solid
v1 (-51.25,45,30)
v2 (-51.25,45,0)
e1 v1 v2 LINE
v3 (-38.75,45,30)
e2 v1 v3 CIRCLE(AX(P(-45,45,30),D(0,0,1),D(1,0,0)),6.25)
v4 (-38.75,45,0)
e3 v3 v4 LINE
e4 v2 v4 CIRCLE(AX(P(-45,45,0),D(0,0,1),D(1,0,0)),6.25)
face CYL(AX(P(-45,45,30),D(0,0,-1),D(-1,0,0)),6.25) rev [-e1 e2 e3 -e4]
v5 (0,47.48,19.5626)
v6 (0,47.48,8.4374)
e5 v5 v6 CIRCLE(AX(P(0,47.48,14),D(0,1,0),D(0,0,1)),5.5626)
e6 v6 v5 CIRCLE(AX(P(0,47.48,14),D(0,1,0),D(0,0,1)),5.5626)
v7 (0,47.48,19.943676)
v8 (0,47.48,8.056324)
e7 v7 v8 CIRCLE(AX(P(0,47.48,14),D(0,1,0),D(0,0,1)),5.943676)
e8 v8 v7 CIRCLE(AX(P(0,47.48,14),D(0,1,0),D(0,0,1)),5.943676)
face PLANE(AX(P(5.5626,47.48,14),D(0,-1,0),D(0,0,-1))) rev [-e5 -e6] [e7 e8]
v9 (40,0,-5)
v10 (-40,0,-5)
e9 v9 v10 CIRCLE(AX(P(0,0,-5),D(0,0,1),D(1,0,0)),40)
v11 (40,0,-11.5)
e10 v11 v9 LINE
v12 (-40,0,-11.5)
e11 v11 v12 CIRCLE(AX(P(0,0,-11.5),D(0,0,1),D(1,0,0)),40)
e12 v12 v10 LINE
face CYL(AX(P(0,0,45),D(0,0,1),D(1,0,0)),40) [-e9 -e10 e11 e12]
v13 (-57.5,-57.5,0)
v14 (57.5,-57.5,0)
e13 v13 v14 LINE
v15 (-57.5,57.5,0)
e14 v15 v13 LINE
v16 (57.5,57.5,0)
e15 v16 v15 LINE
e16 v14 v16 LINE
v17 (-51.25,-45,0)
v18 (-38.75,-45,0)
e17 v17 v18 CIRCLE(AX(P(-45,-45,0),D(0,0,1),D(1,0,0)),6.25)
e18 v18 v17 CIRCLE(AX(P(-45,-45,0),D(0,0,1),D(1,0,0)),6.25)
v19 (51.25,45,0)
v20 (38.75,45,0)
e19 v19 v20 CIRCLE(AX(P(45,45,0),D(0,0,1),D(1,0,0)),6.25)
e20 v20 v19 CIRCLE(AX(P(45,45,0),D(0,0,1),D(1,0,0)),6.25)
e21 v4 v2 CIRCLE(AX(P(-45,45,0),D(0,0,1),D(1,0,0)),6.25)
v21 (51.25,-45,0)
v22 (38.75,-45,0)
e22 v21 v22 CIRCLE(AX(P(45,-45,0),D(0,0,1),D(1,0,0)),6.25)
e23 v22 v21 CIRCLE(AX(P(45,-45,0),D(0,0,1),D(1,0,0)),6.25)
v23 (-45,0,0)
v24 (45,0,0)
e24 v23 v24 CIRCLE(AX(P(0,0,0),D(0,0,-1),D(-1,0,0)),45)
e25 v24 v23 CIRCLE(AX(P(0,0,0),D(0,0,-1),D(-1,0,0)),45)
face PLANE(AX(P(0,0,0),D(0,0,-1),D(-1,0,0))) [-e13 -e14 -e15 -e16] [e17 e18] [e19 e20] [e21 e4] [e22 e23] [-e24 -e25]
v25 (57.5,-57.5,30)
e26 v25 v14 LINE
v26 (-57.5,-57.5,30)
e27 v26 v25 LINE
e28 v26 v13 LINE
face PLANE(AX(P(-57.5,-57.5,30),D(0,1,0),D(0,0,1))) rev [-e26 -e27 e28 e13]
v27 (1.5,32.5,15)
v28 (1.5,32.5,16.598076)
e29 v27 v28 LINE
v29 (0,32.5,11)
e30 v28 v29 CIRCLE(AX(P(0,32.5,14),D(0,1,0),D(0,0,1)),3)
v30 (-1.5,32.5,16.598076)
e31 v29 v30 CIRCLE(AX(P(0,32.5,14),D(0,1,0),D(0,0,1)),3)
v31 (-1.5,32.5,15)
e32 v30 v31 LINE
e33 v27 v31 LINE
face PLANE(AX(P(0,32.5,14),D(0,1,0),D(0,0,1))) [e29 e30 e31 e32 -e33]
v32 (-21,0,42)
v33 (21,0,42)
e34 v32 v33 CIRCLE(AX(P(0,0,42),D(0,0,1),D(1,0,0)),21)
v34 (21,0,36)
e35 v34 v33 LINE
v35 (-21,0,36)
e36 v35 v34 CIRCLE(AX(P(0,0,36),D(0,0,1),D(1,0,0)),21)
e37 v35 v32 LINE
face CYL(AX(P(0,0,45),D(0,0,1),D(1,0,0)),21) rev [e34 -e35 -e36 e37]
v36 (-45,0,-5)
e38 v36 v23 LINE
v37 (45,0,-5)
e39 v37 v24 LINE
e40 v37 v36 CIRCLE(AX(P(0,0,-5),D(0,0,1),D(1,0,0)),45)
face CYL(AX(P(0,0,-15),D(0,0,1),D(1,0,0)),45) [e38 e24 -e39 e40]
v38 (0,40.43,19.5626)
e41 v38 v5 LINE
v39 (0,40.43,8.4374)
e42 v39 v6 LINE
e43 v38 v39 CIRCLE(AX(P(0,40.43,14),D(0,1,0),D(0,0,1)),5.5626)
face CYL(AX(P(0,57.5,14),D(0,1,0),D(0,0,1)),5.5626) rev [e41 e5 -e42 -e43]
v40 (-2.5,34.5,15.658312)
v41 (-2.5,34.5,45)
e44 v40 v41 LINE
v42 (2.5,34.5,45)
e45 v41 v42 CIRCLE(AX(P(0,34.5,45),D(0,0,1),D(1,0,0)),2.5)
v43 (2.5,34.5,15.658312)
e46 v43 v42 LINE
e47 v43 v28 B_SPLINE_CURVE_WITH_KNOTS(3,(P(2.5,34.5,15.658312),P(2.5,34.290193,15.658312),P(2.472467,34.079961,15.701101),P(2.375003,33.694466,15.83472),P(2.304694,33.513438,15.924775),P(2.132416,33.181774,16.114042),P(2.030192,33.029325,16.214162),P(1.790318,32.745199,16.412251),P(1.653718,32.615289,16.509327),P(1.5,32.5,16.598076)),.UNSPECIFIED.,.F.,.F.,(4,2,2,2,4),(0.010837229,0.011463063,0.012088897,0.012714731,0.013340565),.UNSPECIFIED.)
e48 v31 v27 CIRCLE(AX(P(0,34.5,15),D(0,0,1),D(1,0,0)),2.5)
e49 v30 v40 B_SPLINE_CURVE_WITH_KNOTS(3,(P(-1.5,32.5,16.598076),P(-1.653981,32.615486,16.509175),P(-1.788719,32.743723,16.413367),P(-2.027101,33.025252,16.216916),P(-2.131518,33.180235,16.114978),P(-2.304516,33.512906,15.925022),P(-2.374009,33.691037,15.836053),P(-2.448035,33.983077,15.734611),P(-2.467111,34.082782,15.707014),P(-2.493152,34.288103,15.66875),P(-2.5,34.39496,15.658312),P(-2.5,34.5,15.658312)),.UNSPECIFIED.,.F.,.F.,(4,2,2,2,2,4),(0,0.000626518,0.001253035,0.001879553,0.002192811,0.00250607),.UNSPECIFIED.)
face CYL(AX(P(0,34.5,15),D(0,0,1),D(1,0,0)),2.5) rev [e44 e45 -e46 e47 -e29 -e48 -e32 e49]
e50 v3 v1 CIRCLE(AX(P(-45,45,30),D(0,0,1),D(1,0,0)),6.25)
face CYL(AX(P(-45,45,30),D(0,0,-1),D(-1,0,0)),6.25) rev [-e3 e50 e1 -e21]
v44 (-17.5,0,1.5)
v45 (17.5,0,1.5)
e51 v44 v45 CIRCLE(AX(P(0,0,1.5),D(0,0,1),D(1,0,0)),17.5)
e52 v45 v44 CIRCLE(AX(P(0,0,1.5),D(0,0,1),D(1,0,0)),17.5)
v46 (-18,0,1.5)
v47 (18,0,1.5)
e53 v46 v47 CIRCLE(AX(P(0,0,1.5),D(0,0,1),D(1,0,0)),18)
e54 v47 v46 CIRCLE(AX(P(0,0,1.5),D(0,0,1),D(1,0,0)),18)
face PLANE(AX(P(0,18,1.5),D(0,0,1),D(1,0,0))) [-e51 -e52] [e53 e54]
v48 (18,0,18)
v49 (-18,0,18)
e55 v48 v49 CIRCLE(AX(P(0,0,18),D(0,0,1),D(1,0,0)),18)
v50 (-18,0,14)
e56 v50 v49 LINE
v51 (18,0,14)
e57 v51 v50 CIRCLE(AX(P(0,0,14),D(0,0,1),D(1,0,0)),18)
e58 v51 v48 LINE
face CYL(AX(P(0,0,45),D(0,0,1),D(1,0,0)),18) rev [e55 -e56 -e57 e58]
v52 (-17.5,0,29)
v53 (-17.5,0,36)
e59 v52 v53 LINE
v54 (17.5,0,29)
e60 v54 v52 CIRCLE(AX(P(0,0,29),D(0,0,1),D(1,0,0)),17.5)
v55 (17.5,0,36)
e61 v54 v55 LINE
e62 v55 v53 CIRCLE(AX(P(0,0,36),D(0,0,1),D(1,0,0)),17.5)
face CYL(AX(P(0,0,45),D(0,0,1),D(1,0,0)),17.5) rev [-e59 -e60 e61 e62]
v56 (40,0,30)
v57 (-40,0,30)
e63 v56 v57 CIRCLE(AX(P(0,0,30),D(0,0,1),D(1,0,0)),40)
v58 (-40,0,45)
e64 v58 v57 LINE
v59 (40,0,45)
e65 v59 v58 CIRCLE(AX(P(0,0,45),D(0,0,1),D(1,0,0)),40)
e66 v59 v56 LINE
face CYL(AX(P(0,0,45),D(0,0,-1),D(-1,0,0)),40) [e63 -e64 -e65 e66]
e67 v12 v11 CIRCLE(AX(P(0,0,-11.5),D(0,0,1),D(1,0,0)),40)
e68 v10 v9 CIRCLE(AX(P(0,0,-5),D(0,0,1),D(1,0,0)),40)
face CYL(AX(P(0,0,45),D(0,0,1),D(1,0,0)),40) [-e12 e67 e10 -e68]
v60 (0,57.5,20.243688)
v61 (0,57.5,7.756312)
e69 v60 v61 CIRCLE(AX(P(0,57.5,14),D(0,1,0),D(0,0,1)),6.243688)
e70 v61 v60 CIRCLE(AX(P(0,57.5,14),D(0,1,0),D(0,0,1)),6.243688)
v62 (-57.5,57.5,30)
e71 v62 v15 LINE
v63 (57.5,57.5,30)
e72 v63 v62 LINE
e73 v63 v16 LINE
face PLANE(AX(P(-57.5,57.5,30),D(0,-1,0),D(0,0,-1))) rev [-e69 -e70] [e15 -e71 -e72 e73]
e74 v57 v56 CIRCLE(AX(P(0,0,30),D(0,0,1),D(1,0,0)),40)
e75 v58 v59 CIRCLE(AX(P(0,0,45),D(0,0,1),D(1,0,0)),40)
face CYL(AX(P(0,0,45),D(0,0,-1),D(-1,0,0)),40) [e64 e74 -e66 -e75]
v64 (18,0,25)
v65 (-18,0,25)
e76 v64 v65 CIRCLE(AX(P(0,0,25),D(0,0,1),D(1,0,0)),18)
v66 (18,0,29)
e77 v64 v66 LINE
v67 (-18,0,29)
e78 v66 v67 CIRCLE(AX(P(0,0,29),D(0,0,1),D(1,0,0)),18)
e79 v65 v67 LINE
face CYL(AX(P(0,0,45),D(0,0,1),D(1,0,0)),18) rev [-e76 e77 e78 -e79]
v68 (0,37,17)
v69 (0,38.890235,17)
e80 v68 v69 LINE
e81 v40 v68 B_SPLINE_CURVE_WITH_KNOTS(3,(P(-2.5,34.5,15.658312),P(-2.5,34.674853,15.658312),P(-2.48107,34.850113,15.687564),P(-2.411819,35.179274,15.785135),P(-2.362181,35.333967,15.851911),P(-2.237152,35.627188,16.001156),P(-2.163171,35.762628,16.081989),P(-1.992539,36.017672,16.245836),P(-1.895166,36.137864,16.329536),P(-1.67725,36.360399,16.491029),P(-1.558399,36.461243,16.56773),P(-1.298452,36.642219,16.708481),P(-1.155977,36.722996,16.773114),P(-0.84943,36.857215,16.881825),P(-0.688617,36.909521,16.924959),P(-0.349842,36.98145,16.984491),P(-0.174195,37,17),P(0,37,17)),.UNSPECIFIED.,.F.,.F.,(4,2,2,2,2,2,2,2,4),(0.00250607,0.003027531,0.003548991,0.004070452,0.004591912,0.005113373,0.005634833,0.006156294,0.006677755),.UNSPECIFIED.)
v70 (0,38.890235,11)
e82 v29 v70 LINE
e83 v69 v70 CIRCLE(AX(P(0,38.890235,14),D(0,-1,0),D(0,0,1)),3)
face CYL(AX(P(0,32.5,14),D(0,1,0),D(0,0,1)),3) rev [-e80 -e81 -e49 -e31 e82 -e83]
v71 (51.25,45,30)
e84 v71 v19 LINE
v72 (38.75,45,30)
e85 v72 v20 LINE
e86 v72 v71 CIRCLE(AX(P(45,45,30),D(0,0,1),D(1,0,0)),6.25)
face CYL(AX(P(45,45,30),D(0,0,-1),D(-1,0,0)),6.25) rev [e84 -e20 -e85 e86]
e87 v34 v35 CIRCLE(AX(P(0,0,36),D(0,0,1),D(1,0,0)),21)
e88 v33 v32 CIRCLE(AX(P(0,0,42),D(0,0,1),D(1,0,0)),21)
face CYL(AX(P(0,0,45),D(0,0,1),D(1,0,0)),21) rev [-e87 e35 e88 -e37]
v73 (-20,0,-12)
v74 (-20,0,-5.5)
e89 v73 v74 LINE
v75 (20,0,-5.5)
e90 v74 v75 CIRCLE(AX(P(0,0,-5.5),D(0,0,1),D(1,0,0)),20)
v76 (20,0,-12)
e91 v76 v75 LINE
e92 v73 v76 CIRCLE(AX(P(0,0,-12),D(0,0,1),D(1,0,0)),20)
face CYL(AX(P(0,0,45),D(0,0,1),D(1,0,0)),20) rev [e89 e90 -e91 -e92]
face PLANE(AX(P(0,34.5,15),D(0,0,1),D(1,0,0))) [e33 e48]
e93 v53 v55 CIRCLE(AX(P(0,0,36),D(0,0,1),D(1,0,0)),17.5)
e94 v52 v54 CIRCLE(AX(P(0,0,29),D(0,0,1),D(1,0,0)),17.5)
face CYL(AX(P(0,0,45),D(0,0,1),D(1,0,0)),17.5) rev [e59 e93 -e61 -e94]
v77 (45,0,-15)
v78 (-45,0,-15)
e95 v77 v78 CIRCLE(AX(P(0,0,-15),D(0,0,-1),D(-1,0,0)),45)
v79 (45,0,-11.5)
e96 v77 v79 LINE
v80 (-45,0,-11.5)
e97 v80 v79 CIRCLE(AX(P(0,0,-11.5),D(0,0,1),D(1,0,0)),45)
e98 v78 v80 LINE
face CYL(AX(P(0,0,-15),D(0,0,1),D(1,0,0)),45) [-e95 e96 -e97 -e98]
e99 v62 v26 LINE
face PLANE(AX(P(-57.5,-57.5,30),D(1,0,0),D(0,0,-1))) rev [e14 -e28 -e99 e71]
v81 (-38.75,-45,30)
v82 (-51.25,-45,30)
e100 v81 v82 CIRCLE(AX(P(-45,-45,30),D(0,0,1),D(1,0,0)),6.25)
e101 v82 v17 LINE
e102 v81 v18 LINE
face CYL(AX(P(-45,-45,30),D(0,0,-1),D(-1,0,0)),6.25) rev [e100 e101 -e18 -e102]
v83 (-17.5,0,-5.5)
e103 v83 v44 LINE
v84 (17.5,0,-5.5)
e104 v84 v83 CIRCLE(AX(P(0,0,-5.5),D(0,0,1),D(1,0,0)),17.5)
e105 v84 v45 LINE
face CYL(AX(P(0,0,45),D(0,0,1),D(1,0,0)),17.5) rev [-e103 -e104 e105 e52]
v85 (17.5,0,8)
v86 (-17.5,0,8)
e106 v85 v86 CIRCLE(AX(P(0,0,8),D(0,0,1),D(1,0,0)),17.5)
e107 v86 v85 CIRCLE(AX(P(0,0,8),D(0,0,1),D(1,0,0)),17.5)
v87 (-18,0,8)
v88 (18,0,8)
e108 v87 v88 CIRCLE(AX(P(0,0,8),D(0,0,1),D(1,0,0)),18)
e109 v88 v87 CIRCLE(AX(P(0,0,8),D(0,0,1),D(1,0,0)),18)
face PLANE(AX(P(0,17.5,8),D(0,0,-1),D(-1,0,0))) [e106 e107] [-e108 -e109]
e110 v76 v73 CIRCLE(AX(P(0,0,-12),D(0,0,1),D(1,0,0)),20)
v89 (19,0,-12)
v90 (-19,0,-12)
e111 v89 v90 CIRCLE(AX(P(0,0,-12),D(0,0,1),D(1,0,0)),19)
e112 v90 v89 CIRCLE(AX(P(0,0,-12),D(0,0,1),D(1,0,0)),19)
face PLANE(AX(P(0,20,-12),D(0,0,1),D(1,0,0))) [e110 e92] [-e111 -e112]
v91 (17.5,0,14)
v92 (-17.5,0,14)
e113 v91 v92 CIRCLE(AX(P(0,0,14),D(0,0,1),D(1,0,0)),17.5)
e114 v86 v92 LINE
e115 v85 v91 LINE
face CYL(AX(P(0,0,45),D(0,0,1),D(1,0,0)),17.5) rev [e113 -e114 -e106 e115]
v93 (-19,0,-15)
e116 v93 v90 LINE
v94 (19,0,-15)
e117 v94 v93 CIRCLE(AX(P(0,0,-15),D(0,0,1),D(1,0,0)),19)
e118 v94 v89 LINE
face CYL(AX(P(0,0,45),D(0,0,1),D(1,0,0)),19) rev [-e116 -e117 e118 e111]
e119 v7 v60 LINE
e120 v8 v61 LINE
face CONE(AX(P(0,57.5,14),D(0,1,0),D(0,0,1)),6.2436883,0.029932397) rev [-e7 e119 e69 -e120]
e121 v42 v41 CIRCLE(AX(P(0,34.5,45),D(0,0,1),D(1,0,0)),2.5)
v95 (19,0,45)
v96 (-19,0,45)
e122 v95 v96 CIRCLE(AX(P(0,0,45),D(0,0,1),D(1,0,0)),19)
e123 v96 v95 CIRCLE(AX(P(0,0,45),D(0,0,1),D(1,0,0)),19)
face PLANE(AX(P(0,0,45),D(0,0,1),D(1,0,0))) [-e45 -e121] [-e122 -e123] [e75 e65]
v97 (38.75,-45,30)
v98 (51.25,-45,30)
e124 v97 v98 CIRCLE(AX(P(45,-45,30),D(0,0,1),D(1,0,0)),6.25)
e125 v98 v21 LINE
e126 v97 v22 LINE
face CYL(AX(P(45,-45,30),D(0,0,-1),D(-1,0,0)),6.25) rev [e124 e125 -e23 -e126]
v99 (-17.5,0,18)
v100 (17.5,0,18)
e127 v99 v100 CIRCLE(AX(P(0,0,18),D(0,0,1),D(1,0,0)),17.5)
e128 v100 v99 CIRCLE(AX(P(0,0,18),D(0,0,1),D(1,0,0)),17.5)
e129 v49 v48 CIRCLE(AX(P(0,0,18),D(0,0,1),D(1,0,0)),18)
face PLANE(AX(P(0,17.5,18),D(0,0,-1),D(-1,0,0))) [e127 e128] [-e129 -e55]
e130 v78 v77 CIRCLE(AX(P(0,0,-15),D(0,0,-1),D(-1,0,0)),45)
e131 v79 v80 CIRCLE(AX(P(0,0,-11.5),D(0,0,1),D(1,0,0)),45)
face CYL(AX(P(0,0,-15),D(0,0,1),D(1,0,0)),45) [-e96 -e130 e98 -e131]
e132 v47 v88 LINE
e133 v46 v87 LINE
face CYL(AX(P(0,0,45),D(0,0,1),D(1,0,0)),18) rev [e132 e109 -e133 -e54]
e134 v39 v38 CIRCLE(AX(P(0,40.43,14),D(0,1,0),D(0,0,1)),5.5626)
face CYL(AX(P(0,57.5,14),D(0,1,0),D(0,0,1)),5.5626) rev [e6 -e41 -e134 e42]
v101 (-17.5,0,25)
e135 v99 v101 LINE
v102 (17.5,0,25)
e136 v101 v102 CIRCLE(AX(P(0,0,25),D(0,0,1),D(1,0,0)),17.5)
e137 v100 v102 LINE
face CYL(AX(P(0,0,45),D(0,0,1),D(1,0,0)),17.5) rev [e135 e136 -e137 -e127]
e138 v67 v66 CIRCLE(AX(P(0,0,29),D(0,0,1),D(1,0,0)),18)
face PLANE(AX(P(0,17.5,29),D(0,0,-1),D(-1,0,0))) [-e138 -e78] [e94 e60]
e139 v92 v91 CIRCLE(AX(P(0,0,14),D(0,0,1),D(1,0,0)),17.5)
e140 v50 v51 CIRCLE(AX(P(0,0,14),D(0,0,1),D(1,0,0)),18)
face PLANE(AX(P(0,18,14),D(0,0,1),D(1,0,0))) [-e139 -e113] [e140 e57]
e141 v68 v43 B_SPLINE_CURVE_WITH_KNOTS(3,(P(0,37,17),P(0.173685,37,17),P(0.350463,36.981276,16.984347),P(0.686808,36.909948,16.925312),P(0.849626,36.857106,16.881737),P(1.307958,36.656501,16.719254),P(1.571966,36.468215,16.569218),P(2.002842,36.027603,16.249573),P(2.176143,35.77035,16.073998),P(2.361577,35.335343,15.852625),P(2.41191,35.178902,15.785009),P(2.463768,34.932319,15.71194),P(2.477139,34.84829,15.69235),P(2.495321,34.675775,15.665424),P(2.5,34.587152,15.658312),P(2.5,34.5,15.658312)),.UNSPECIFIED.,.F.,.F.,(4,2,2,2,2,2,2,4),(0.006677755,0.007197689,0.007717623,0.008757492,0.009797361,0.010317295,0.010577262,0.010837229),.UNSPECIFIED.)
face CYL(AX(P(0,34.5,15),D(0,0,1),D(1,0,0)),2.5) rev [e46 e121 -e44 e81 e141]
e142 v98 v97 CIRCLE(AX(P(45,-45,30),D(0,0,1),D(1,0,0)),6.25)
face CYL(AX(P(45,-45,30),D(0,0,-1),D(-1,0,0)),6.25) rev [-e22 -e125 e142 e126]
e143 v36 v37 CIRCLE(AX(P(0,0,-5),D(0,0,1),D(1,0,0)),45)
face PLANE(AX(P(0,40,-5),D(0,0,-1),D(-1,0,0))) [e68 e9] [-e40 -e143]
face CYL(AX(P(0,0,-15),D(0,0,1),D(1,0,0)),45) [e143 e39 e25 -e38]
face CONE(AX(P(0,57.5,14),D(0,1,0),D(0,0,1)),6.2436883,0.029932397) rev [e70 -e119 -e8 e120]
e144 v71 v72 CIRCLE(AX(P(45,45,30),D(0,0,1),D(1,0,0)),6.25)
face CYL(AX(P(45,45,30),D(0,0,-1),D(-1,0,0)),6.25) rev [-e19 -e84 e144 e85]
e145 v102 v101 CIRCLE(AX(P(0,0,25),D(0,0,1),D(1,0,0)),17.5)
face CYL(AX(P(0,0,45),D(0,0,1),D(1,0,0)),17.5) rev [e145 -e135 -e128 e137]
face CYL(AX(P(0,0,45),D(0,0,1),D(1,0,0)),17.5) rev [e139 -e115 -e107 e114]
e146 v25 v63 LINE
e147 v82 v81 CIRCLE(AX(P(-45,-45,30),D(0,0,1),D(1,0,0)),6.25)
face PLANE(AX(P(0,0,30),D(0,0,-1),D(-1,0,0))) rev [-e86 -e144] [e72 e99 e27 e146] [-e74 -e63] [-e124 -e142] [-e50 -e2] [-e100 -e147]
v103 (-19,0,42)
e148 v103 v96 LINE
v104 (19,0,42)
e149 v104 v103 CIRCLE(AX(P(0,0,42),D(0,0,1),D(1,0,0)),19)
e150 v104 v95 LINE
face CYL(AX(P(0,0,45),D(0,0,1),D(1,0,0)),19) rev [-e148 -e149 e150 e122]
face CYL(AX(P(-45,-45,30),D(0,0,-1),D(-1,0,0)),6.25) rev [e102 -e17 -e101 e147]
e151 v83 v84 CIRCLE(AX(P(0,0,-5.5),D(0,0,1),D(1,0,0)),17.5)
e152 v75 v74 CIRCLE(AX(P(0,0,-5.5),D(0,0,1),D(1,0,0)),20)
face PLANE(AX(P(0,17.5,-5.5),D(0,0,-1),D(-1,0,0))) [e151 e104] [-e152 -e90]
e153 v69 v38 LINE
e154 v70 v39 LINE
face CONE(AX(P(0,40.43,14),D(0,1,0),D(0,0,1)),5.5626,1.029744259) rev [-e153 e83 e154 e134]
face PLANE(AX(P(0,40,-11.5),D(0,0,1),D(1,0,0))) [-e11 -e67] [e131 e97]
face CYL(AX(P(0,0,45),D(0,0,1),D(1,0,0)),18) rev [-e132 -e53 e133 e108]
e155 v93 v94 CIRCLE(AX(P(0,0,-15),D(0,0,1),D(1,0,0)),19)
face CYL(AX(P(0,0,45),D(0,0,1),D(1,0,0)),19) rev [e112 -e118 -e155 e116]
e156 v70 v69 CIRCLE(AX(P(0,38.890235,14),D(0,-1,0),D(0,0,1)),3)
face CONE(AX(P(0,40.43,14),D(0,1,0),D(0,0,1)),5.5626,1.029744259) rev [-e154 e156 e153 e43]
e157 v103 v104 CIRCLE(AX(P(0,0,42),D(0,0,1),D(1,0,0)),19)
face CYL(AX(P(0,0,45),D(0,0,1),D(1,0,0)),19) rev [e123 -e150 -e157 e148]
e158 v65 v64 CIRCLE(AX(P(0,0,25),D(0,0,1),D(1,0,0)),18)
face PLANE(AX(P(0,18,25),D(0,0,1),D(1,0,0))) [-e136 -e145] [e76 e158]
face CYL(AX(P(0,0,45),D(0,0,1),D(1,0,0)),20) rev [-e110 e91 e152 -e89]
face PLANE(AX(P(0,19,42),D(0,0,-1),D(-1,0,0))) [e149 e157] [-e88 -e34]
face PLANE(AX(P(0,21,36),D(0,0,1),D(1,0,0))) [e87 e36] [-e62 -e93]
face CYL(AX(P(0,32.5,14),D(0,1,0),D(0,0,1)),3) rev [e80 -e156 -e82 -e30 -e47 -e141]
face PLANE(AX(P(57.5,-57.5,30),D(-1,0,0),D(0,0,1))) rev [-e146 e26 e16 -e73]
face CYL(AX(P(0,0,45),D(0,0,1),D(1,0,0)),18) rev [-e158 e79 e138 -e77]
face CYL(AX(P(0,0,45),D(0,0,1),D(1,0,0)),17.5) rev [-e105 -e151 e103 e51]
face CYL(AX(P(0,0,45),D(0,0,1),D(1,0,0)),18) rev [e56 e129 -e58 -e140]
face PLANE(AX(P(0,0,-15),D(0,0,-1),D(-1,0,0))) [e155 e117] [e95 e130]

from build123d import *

# Parameters (mm, degrees)
SKETCH_1_W          = 115
SKETCH_1_H          = 115
SKETCH_1_R          = 6.25
EXTRUDE_1_DEPTH     = 30
SKETCH_2_R          = 40
EXTRUDE_2_DEPTH     = 15
SKETCH_22_R         = 45
EXTRUDE_4_DEPTH     = 15
SKETCH_23_W         = 6.5
SKETCH_23_H         = 5
SKETCH_24_R         = 2.5
CUT_EXTRUDE_5_DEPTH = 30
SKETCH_28_R         = 3
CUT_EXTRUDE_6_DEPTH = 25


with BuildPart() as part:
    # 草图1 → 凸台-拉伸1 (new body)
    with BuildSketch(Plane.XY):
        Rectangle(SKETCH_1_W, SKETCH_1_H)
        with Locations((-45, 45)):
            Circle(SKETCH_1_R, mode=Mode.SUBTRACT)
        with Locations((45, 45)):
            Circle(SKETCH_1_R, mode=Mode.SUBTRACT)
        with Locations((45, -45)):
            Circle(SKETCH_1_R, mode=Mode.SUBTRACT)
        with Locations((-45, -45)):
            Circle(SKETCH_1_R, mode=Mode.SUBTRACT)
    extrude(amount=EXTRUDE_1_DEPTH)

    # 草图2 → 凸台-拉伸2 (add)
    with BuildSketch(Plane.XY.offset(30)):
        Circle(SKETCH_2_R)
    extrude(amount=EXTRUDE_2_DEPTH)

    # 草图22 → 凸台-拉伸4 (add)
    with BuildSketch(Plane(origin=(0, 0, 0), x_dir=(-1, 0, 0), z_dir=(0, 0, -1))):
        Circle(SKETCH_22_R)
    extrude(amount=EXTRUDE_4_DEPTH)

    # 草图23 → 切除-旋转2 (revolve, cut)
    with BuildSketch(Plane(origin=(0, 0, 0), x_dir=(0, 0, -1), z_dir=(1, 0, 0)), mode=Mode.PRIVATE) as cut_revolve_2_sk:
        Polygon((-45, 19), (-42, 19), (-42, 21), (-36, 21), (-36, 17.5), (-29, 17.5), (-29, 18), (-25, 18), (-25, 17.5), (-18, 17.5), (-18, 18), (-14, 18), (-14, 17.5), (-8, 17.5), (-8, 18), (-1.5, 18), (-1.5, 17.5), (5.5, 17.5), (5.5, 20), (12, 20), (12, 19), (15, 19), (15, 0), (-45, 0), align=None)
        with Locations((8.25, 42.5)):
            Rectangle(SKETCH_23_W, SKETCH_23_H)
    revolve(cut_revolve_2_sk.sketch.rotate(Axis((0, 0, 45), (0, 0, -1)), 90), axis=Axis((0, 0, 45), (0, 0, -1)), mode=Mode.SUBTRACT)

    # 草图24 → 切除-拉伸5 (cut)
    with BuildSketch(Plane.XY.offset(45)):
        with Locations((0, 34.5)):
            Circle(SKETCH_24_R)
    extrude(amount=-CUT_EXTRUDE_5_DEPTH, mode=Mode.SUBTRACT)

    # 草图26 → 1/4 NPT 螺纹孔2 (revolve, cut)
    with BuildSketch(Plane(origin=(0, 57.5, 14), x_dir=(0, 0, 1), z_dir=(1, 0, 0))):
        Polygon((0, 0), (0, 20.412347279), (5.5626, 17.07), (5.5626, 10.02), (5.943676082, 10.02), (6.2436883, 0), align=None)
    revolve(axis=Axis((0, 63.85, 14), (0, -1, 0)), mode=Mode.SUBTRACT)

    # 草图28 → 切除-拉伸6 (cut)
    with BuildSketch(Plane(origin=(0, 57.5, 0), x_dir=(1, 0, 0), z_dir=(0, 1, 0))):
        with Locations(Location((0, -14, 0), (0, 0, 270))):
            Circle(SKETCH_28_R)
    extrude(amount=-CUT_EXTRUDE_6_DEPTH, mode=Mode.SUBTRACT)


solid = part.part
